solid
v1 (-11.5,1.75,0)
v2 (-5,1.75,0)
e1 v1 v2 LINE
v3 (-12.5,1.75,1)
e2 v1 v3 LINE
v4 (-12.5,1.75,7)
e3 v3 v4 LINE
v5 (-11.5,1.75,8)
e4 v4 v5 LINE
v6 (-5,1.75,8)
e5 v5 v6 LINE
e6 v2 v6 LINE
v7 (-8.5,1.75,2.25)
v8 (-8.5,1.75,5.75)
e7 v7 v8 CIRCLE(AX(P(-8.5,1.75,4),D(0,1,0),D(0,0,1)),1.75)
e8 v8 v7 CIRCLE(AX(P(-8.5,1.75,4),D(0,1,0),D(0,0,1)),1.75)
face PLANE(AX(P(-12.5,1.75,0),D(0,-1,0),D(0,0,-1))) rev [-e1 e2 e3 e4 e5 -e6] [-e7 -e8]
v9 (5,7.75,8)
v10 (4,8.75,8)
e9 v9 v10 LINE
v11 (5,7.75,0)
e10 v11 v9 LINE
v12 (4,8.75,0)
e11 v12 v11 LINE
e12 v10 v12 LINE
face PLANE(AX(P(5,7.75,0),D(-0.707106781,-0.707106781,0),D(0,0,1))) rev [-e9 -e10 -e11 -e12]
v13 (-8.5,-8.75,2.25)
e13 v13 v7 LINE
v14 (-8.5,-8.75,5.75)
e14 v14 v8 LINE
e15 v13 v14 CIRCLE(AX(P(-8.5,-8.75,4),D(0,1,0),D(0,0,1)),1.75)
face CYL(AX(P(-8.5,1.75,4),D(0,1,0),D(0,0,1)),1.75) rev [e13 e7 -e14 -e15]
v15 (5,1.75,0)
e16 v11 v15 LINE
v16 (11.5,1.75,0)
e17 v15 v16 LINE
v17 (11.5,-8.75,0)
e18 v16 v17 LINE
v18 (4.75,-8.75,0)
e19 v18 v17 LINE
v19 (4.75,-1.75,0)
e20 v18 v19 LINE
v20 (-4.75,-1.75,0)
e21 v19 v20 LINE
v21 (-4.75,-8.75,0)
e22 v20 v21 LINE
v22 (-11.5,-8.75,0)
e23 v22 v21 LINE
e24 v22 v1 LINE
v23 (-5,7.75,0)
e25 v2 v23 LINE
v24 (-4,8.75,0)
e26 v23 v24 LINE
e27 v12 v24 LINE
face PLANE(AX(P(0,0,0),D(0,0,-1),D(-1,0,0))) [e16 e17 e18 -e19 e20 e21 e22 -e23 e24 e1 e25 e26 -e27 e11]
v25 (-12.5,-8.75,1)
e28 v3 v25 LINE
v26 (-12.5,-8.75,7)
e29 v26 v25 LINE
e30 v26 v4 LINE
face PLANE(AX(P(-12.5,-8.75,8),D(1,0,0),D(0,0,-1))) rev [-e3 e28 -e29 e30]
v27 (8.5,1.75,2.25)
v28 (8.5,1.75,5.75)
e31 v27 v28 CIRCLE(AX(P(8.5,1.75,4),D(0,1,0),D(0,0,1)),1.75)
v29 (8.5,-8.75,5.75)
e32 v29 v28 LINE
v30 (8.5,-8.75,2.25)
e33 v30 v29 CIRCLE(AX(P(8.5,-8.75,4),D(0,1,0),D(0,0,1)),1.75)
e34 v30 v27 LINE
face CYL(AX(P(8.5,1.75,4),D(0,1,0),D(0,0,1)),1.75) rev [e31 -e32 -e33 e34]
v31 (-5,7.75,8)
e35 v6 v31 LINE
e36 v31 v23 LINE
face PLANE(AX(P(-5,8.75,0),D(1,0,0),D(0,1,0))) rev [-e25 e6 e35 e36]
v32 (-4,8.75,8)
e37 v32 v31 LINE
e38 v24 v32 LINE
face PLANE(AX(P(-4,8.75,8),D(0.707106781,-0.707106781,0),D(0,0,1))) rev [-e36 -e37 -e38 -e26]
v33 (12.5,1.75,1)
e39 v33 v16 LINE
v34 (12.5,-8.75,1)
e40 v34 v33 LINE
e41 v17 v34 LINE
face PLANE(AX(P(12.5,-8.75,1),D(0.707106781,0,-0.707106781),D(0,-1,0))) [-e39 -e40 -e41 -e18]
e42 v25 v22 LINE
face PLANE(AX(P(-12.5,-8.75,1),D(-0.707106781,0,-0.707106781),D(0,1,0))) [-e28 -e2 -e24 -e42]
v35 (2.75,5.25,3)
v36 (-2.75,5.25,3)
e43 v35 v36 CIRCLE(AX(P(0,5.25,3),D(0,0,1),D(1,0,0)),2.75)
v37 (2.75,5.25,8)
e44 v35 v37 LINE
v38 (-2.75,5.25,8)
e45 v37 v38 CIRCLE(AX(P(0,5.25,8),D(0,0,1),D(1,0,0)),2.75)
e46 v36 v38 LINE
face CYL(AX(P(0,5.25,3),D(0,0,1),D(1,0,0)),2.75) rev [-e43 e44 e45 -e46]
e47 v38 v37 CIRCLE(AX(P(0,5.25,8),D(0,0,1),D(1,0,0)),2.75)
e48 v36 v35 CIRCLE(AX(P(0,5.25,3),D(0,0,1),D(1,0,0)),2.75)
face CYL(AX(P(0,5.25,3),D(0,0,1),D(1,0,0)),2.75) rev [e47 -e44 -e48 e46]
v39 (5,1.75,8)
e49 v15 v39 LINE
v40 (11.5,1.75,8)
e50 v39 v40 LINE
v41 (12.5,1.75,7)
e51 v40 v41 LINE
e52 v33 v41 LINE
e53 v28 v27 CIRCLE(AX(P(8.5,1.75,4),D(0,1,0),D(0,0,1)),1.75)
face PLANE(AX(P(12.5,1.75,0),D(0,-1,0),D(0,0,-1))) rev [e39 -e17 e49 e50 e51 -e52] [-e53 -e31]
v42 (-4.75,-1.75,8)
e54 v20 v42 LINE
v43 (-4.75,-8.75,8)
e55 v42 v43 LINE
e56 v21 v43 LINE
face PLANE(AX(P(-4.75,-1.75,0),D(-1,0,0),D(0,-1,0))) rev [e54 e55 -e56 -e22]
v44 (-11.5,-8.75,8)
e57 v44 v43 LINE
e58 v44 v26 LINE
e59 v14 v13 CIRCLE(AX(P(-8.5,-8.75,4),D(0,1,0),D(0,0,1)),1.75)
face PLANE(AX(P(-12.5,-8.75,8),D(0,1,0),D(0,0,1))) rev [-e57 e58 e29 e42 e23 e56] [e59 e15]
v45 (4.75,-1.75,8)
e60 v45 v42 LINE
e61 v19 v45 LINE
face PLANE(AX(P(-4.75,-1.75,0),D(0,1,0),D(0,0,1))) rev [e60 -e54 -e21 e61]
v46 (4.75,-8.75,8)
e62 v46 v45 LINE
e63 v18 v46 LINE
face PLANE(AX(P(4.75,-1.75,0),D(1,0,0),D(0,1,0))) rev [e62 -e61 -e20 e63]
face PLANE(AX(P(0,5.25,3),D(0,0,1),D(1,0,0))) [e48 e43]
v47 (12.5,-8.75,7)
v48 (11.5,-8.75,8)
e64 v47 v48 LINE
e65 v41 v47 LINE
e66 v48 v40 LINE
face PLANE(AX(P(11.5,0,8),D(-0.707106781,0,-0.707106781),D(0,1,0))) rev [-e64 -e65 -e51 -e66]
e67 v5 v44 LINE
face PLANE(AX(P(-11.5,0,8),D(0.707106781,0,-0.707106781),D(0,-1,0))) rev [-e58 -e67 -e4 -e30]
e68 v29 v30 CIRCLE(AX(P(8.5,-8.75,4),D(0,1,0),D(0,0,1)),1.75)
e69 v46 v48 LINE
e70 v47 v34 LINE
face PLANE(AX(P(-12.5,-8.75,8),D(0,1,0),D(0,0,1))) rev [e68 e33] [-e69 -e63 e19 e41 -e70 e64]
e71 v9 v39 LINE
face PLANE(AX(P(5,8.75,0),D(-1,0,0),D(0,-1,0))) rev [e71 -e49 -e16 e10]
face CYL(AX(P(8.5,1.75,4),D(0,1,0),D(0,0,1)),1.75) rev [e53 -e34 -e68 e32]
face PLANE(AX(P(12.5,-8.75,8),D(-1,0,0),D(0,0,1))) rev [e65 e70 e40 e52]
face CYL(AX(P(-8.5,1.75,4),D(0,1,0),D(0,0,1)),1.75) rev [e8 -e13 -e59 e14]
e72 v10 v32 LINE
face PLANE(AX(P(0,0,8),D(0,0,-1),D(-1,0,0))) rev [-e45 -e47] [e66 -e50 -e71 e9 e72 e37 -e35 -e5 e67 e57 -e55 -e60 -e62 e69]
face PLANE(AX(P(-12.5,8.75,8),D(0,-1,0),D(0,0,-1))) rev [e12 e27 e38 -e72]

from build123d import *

# Parameters (mm, degrees)
SKETCH1_W                  = 25
SKETCH1_H                  = 17.5
BOSS_EXTRUDE1_DEPTH        = 8
SKETCH2_W                  = 7.5
SKETCH2_H                  = 7
CUT_EXTRUDE1_DEPTH         = 8
SKETCH3_W                  = 9.5
SKETCH3_H                  = 7
CUT_EXTRUDE2_DEPTH         = 18.228247154
SKETCH4_R                  = 2.75
CUT_EXTRUDE3_DEPTH         = 5
F_3_5_3_5_DIAMETER_HOLE1_D = 3.5
CHAMFER1_SIZE              = 1


with BuildPart() as part:
    # Sketch1 → Boss-Extrude1 (new body)
    with BuildSketch(Plane.XY):
        Rectangle(SKETCH1_W, SKETCH1_H)
    extrude(amount=BOSS_EXTRUDE1_DEPTH)

    # Sketch2 → Cut-Extrude1 (cut)
    with BuildSketch(Plane.XY.offset(8)):
        with Locations((8.75, 5.25)):
            Rectangle(SKETCH2_W, SKETCH2_H)
        with Locations((-8.75, 5.25)):
            Rectangle(SKETCH2_W, SKETCH2_H)
    extrude(amount=-CUT_EXTRUDE1_DEPTH, mode=Mode.SUBTRACT)

    # Sketch3 → Cut-Extrude2 (cut, through all)
    with BuildSketch(Plane.XY.offset(8)):
        with Locations((0, -5.25)):
            Rectangle(SKETCH3_W, SKETCH3_H)
    extrude(amount=-CUT_EXTRUDE2_DEPTH, mode=Mode.SUBTRACT)

    # Sketch4 → Cut-Extrude3 (cut)
    with BuildSketch(Plane.XY.offset(8)):
        with Locations((0, 5.25)):
            Circle(SKETCH4_R)
    extrude(amount=-CUT_EXTRUDE3_DEPTH, mode=Mode.SUBTRACT)

    # Ø3.5 (3.5) Diameter Hole1 (through all)
    with Locations(Plane(origin=(0, 1.75, 0), x_dir=(1, 0, 0), z_dir=(0, 1, 0))):
        with Locations((-8.5, -4), (8.5, -4)):
            Hole(F_3_5_3_5_DIAMETER_HOLE1_D / 2)

    # Chamfer1
    chamfer1_edges = [part.edges().sort_by_distance(p)[0] for p in [
        (-12.5, -3.5, 0),
        (-12.5, -3.5, 8),
        (-5, 8.75, 4),
        (5, 8.75, 4),
        (12.5, -3.5, 8),
        (12.5, -3.5, 0),
    ]]
    chamfer(chamfer1_edges, length=CHAMFER1_SIZE)


solid = part.part
